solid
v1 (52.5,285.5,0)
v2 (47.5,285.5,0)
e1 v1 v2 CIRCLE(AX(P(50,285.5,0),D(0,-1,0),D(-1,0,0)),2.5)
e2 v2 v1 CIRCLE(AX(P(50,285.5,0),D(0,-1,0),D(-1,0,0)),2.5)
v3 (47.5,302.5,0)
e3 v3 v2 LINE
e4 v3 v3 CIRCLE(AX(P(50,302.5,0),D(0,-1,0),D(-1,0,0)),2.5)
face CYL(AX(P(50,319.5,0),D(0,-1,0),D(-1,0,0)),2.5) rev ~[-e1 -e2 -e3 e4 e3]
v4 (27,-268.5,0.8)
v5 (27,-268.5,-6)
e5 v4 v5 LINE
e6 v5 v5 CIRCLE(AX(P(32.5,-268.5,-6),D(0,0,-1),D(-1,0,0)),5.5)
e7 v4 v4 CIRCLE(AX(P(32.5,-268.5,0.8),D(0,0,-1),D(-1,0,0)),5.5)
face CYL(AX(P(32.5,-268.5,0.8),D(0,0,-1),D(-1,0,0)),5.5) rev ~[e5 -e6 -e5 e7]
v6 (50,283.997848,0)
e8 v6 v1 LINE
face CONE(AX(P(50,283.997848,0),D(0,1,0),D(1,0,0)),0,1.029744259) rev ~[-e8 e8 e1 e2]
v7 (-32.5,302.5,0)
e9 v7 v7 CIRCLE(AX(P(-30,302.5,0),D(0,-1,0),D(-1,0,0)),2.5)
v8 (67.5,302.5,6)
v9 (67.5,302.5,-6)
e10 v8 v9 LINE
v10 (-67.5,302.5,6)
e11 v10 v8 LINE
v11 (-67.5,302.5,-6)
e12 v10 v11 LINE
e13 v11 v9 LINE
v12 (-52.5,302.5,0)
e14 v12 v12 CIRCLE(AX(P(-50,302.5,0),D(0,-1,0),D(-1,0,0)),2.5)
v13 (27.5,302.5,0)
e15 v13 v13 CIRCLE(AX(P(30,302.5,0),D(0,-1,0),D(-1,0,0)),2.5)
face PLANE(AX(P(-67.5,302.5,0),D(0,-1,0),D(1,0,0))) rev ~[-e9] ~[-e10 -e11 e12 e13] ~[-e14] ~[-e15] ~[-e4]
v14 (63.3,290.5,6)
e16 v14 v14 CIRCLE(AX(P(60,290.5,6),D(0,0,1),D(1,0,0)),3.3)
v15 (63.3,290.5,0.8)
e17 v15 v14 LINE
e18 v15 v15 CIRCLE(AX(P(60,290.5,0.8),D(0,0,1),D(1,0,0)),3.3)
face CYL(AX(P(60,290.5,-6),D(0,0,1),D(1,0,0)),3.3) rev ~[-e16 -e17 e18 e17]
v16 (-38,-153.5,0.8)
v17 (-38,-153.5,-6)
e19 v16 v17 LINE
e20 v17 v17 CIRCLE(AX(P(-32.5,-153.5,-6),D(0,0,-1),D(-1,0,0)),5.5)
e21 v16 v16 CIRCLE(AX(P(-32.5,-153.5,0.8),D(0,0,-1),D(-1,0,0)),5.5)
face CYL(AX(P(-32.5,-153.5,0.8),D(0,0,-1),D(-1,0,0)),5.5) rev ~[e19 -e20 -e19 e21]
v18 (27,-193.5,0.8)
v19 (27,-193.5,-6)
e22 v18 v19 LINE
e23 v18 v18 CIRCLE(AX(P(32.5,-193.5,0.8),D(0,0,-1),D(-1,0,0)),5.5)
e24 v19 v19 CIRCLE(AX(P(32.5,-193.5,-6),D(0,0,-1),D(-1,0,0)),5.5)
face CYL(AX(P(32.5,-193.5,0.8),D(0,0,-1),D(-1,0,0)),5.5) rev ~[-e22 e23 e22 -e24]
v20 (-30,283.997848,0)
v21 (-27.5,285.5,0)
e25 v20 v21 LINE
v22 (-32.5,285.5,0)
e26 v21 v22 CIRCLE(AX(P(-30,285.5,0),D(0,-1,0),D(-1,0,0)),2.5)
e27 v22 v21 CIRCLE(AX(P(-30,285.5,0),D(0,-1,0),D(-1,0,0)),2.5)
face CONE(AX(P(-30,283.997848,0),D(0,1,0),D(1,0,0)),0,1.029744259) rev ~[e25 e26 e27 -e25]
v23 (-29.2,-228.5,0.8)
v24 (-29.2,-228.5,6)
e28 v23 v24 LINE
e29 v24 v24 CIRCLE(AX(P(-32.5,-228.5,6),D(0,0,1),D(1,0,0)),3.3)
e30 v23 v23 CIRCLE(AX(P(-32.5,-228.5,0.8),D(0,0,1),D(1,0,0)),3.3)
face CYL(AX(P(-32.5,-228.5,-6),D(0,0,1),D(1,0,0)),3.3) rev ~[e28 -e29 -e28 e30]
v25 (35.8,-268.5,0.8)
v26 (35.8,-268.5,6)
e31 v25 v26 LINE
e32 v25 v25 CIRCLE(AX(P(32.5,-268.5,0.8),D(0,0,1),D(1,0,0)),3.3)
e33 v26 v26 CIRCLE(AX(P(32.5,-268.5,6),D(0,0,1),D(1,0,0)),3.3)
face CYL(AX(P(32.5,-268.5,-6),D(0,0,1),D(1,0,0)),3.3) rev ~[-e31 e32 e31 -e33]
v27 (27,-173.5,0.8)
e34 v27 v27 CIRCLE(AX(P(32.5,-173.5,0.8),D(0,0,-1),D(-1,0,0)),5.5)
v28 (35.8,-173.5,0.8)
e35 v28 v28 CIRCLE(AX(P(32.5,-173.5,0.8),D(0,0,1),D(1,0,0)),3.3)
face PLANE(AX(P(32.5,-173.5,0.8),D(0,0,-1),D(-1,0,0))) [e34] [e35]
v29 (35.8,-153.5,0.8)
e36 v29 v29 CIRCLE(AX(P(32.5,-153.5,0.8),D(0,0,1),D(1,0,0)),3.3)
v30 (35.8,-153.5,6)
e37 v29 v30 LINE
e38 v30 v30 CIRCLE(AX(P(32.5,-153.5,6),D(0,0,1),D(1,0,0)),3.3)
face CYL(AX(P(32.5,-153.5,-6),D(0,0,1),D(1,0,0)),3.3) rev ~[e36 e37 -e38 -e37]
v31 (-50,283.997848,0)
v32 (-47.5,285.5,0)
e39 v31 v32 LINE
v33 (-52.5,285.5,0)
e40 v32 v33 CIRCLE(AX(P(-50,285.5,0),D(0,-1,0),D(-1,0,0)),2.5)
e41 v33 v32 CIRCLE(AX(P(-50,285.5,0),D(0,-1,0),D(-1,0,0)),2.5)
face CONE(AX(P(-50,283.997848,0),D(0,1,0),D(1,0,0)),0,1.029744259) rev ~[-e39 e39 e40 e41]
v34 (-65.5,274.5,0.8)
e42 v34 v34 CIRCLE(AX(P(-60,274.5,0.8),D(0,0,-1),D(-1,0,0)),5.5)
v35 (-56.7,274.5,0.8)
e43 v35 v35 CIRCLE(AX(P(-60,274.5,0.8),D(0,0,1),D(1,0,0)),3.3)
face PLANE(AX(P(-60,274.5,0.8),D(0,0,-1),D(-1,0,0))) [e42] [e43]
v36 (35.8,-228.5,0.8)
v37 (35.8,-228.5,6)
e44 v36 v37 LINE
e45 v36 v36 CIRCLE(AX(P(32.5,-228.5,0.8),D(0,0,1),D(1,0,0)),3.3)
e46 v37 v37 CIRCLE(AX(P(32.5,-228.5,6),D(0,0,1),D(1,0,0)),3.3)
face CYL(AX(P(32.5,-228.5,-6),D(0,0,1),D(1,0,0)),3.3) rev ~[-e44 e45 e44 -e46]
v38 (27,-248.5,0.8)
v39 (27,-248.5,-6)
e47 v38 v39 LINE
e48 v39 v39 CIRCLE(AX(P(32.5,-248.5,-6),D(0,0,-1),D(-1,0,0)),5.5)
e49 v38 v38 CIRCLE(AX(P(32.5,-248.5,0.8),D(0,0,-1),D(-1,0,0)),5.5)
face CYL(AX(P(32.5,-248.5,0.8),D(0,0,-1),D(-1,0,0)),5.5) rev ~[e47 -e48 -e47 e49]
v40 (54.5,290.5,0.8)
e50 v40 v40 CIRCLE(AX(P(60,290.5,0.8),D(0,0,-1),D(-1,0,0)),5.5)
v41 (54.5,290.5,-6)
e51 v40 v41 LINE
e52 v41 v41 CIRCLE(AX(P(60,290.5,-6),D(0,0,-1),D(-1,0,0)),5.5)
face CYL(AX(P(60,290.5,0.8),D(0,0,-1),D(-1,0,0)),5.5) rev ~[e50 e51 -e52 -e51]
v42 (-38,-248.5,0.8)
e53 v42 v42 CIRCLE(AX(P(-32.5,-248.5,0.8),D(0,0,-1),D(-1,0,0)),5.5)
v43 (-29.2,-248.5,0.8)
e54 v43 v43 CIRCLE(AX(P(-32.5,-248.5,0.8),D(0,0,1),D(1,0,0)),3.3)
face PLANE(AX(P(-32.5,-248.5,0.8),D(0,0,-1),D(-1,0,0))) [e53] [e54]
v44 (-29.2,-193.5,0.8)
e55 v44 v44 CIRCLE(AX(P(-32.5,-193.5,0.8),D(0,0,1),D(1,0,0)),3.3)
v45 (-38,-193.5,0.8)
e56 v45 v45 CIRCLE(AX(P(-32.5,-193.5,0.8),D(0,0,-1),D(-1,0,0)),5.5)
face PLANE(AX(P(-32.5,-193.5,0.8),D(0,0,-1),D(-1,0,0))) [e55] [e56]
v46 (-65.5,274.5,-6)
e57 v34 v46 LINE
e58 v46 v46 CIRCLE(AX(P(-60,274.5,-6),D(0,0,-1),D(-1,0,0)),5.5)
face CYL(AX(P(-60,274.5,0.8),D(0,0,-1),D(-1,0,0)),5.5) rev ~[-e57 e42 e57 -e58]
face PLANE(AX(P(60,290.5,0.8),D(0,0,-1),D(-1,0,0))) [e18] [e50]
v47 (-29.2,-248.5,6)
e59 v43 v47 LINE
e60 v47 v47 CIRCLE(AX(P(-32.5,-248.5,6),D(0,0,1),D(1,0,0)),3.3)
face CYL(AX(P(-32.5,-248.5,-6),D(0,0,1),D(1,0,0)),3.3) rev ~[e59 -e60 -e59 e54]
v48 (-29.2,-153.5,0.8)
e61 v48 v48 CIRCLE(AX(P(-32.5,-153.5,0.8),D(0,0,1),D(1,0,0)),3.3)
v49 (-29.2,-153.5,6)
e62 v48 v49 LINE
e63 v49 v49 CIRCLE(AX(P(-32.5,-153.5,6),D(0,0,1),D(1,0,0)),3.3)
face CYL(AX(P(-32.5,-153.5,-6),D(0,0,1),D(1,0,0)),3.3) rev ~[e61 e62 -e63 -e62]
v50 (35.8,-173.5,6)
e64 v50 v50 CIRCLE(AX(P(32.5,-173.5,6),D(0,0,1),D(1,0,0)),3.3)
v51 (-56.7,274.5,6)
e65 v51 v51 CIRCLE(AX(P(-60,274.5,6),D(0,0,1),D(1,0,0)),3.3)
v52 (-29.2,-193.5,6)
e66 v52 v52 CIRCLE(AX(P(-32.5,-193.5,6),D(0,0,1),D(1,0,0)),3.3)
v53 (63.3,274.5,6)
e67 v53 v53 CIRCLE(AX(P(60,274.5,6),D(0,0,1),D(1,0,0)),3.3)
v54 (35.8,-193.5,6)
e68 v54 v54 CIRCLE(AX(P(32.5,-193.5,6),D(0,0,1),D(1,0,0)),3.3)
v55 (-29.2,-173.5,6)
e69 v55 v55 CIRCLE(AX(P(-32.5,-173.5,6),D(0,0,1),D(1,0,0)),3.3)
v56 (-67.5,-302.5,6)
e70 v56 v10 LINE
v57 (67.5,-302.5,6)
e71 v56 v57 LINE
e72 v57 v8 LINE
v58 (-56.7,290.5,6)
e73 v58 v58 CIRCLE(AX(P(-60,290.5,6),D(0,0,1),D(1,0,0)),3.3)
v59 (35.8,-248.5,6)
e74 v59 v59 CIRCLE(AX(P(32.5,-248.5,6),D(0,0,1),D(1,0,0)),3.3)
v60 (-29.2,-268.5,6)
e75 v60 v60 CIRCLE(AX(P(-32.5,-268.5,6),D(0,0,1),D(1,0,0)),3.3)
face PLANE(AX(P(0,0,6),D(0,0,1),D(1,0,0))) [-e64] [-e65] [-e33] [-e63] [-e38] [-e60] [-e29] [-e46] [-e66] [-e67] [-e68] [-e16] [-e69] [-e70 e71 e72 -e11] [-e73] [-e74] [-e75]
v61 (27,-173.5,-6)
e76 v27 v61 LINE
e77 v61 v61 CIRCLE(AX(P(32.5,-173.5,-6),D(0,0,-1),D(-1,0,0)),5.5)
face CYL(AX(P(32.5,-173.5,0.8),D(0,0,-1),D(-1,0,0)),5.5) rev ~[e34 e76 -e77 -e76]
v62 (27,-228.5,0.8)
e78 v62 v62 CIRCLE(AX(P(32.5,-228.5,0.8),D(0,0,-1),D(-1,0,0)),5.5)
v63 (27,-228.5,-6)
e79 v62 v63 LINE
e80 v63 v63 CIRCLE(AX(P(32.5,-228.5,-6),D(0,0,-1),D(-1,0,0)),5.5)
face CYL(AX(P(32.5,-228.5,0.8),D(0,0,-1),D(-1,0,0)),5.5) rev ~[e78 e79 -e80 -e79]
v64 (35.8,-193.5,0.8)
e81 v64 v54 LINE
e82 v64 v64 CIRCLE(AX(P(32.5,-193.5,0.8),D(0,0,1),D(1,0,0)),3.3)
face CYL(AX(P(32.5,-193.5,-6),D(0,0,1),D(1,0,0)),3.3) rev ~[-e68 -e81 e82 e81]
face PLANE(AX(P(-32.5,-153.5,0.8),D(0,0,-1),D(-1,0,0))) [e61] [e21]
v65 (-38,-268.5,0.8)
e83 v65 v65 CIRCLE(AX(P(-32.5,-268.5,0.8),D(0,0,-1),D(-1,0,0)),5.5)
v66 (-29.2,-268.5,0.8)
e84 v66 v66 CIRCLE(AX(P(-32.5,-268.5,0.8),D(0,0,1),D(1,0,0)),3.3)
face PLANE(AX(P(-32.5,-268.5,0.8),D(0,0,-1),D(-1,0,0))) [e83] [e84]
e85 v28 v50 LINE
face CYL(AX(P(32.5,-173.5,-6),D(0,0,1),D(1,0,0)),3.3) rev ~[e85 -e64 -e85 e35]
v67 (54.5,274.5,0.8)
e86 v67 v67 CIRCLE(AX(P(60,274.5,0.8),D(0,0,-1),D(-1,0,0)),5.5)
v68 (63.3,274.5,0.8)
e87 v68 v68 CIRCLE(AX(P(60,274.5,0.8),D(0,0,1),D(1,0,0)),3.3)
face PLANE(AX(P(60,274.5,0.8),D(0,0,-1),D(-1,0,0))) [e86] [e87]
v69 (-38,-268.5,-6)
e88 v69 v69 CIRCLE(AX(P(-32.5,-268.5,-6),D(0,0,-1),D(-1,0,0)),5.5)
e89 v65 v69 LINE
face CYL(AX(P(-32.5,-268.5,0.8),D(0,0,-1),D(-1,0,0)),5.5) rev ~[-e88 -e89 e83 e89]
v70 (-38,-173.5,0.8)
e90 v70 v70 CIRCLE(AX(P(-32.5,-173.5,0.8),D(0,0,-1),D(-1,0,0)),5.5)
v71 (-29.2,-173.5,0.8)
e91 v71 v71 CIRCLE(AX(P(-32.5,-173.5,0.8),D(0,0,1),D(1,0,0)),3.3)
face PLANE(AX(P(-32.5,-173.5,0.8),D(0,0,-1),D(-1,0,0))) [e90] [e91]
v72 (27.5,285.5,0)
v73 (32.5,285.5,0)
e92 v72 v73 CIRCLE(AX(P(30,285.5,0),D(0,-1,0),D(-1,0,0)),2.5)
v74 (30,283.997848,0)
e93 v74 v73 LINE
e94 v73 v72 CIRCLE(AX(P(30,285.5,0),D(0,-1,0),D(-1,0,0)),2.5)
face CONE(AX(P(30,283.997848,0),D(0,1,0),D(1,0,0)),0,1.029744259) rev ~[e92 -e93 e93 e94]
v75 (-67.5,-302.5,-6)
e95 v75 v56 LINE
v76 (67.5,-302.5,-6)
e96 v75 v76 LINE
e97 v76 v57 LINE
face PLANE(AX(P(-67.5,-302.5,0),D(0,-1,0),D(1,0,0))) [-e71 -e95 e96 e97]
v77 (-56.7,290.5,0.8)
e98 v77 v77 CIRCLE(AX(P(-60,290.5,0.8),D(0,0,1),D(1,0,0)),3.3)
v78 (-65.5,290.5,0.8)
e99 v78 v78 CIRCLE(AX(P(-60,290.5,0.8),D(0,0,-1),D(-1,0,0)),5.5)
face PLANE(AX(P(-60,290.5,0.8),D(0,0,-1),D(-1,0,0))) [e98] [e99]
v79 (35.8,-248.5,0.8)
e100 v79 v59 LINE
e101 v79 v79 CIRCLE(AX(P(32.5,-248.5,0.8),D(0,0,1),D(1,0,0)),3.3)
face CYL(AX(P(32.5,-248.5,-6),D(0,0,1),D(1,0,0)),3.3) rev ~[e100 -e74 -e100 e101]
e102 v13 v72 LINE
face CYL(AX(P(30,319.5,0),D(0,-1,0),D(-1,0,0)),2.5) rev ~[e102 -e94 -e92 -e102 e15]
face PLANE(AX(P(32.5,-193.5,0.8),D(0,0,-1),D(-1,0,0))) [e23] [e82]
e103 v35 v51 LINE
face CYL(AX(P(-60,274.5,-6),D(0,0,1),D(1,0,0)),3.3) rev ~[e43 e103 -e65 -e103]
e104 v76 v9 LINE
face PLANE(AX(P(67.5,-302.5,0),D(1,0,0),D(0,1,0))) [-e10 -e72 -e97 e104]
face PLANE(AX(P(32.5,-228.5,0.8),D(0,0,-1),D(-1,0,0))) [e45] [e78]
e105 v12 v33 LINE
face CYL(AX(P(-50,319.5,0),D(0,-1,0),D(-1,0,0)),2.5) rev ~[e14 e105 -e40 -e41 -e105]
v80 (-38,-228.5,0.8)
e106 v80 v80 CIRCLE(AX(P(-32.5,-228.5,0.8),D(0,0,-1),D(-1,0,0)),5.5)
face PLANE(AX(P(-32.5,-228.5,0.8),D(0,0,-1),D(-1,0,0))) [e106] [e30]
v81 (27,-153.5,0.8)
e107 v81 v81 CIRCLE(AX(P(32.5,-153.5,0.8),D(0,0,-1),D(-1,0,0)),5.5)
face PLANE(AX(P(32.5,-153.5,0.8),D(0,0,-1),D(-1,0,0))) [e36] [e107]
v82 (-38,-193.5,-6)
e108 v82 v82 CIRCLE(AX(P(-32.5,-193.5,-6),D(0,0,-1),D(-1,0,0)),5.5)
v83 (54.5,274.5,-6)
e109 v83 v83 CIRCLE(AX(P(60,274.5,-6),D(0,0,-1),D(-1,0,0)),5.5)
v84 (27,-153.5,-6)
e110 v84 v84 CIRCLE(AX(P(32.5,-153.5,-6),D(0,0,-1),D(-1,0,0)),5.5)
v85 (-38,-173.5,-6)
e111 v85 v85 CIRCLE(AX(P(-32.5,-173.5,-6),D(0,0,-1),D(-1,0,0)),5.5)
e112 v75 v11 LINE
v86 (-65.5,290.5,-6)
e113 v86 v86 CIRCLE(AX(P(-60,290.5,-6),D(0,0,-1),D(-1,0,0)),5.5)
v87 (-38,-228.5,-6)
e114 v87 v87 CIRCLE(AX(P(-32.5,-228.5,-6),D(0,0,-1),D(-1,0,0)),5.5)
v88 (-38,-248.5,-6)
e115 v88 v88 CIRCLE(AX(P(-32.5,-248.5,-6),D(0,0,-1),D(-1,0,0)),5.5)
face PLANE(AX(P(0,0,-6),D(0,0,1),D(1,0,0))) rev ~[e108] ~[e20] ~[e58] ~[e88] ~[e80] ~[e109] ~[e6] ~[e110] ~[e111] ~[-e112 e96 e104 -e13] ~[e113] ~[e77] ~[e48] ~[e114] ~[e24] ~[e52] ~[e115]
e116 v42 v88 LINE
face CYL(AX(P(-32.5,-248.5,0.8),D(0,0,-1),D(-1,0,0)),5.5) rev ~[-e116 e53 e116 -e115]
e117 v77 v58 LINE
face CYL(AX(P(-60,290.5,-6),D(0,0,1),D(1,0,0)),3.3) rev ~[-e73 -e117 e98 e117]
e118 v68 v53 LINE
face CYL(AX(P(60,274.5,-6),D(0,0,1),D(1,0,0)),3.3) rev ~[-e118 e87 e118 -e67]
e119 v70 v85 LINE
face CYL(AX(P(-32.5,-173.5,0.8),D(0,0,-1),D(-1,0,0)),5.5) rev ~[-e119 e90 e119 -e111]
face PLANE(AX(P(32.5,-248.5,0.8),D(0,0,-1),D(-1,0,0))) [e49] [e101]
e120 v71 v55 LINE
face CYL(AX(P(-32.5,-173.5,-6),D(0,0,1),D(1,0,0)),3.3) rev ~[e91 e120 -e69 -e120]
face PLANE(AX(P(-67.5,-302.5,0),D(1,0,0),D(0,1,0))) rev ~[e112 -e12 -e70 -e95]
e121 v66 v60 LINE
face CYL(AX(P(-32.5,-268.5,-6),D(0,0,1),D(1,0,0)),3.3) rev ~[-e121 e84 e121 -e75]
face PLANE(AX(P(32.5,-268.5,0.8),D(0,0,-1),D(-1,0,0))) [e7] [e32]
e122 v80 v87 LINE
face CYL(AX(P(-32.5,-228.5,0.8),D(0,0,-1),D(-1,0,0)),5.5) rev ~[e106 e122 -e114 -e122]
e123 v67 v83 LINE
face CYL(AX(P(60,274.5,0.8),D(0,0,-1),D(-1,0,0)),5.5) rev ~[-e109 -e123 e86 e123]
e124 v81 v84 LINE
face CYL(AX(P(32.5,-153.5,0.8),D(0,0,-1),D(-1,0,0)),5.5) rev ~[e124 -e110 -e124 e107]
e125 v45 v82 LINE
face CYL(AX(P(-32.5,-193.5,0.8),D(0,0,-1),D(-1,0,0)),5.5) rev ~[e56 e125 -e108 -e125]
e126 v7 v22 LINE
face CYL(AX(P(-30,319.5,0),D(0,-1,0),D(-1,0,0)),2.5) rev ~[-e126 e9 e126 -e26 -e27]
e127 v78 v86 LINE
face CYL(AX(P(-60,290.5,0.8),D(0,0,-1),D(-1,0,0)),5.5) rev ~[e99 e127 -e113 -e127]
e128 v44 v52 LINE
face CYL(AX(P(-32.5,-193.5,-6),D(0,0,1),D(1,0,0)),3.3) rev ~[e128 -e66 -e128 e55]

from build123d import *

# Parameters (mm, degrees)
SKETCH_1_W                  = 135
SKETCH_1_H                  = 605
EXTRUDE_1_DEPTH             = 6
HOLE_WIZARD_M6_1_D          = 5
HOLE_WIZARD_M6_1_DEPTH      = 17
HOLE_WIZARD_M6_1_TIP        = 1.502151548
HOLE_WIZARD_2_D             = 6.6
HOLE_WIZARD_2_CBORE_D       = 11
HOLE_WIZARD_2_CBORE_DEPTH   = 6.8
HOLE_WIZARD_2_2_D           = 6.6
HOLE_WIZARD_2_2_CBORE_D     = 11
HOLE_WIZARD_2_2_CBORE_DEPTH = 6.8


with BuildPart() as part:
    # 草图1 → 凸台-拉伸1 (new, symmetric)
    with BuildSketch(Plane.XY):
        Rectangle(SKETCH_1_W, SKETCH_1_H)
    extrude(amount=EXTRUDE_1_DEPTH, both=True)

    # M6 螺纹孔1
    with Locations(Plane(origin=(0, 302.5, 0), x_dir=(1, 0, 0), z_dir=(0, 1, 0))):
        with Locations((50, 0), (-30, 0), (30, 0), (-405, -6), (-50, 0)):
            Hole(HOLE_WIZARD_M6_1_D / 2, depth=HOLE_WIZARD_M6_1_DEPTH)
            with Locations((0, 0, -(HOLE_WIZARD_M6_1_DEPTH + HOLE_WIZARD_M6_1_TIP / 2))):  # 118° drill point
                Cone(0, HOLE_WIZARD_M6_1_D / 2, HOLE_WIZARD_M6_1_TIP, mode=Mode.SUBTRACT)

    # Hole Wizard 2 (through all)
    with Locations(Plane(origin=(0, 0, -6), x_dir=(-1, 0, 0), z_dir=(0, 0, -1))):
        with Locations((-60, 290.5), (60, 290.5), (-60, 274.5), (60, 274.5)):
            CounterBoreHole(HOLE_WIZARD_2_D / 2, HOLE_WIZARD_2_CBORE_D / 2, HOLE_WIZARD_2_CBORE_DEPTH)

    # Hole Wizard 2 2 (through all)
    with Locations(Plane(origin=(0, 0, -6), x_dir=(-1, 0, 0), z_dir=(0, 0, -1))):
        with Locations((-32.5, -153.5), (-32.5, -228.5), (32.5, -228.5), (32.5, -153.5), (32.5, -173.5), (32.5, -248.5), (-32.5, -248.5), (-32.5, -173.5), (32.5, -268.5), (32.5, -193.5), (-32.5, -193.5), (-32.5, -268.5)):
            CounterBoreHole(HOLE_WIZARD_2_2_D / 2, HOLE_WIZARD_2_2_CBORE_D / 2, HOLE_WIZARD_2_2_CBORE_DEPTH)


solid = part.part
